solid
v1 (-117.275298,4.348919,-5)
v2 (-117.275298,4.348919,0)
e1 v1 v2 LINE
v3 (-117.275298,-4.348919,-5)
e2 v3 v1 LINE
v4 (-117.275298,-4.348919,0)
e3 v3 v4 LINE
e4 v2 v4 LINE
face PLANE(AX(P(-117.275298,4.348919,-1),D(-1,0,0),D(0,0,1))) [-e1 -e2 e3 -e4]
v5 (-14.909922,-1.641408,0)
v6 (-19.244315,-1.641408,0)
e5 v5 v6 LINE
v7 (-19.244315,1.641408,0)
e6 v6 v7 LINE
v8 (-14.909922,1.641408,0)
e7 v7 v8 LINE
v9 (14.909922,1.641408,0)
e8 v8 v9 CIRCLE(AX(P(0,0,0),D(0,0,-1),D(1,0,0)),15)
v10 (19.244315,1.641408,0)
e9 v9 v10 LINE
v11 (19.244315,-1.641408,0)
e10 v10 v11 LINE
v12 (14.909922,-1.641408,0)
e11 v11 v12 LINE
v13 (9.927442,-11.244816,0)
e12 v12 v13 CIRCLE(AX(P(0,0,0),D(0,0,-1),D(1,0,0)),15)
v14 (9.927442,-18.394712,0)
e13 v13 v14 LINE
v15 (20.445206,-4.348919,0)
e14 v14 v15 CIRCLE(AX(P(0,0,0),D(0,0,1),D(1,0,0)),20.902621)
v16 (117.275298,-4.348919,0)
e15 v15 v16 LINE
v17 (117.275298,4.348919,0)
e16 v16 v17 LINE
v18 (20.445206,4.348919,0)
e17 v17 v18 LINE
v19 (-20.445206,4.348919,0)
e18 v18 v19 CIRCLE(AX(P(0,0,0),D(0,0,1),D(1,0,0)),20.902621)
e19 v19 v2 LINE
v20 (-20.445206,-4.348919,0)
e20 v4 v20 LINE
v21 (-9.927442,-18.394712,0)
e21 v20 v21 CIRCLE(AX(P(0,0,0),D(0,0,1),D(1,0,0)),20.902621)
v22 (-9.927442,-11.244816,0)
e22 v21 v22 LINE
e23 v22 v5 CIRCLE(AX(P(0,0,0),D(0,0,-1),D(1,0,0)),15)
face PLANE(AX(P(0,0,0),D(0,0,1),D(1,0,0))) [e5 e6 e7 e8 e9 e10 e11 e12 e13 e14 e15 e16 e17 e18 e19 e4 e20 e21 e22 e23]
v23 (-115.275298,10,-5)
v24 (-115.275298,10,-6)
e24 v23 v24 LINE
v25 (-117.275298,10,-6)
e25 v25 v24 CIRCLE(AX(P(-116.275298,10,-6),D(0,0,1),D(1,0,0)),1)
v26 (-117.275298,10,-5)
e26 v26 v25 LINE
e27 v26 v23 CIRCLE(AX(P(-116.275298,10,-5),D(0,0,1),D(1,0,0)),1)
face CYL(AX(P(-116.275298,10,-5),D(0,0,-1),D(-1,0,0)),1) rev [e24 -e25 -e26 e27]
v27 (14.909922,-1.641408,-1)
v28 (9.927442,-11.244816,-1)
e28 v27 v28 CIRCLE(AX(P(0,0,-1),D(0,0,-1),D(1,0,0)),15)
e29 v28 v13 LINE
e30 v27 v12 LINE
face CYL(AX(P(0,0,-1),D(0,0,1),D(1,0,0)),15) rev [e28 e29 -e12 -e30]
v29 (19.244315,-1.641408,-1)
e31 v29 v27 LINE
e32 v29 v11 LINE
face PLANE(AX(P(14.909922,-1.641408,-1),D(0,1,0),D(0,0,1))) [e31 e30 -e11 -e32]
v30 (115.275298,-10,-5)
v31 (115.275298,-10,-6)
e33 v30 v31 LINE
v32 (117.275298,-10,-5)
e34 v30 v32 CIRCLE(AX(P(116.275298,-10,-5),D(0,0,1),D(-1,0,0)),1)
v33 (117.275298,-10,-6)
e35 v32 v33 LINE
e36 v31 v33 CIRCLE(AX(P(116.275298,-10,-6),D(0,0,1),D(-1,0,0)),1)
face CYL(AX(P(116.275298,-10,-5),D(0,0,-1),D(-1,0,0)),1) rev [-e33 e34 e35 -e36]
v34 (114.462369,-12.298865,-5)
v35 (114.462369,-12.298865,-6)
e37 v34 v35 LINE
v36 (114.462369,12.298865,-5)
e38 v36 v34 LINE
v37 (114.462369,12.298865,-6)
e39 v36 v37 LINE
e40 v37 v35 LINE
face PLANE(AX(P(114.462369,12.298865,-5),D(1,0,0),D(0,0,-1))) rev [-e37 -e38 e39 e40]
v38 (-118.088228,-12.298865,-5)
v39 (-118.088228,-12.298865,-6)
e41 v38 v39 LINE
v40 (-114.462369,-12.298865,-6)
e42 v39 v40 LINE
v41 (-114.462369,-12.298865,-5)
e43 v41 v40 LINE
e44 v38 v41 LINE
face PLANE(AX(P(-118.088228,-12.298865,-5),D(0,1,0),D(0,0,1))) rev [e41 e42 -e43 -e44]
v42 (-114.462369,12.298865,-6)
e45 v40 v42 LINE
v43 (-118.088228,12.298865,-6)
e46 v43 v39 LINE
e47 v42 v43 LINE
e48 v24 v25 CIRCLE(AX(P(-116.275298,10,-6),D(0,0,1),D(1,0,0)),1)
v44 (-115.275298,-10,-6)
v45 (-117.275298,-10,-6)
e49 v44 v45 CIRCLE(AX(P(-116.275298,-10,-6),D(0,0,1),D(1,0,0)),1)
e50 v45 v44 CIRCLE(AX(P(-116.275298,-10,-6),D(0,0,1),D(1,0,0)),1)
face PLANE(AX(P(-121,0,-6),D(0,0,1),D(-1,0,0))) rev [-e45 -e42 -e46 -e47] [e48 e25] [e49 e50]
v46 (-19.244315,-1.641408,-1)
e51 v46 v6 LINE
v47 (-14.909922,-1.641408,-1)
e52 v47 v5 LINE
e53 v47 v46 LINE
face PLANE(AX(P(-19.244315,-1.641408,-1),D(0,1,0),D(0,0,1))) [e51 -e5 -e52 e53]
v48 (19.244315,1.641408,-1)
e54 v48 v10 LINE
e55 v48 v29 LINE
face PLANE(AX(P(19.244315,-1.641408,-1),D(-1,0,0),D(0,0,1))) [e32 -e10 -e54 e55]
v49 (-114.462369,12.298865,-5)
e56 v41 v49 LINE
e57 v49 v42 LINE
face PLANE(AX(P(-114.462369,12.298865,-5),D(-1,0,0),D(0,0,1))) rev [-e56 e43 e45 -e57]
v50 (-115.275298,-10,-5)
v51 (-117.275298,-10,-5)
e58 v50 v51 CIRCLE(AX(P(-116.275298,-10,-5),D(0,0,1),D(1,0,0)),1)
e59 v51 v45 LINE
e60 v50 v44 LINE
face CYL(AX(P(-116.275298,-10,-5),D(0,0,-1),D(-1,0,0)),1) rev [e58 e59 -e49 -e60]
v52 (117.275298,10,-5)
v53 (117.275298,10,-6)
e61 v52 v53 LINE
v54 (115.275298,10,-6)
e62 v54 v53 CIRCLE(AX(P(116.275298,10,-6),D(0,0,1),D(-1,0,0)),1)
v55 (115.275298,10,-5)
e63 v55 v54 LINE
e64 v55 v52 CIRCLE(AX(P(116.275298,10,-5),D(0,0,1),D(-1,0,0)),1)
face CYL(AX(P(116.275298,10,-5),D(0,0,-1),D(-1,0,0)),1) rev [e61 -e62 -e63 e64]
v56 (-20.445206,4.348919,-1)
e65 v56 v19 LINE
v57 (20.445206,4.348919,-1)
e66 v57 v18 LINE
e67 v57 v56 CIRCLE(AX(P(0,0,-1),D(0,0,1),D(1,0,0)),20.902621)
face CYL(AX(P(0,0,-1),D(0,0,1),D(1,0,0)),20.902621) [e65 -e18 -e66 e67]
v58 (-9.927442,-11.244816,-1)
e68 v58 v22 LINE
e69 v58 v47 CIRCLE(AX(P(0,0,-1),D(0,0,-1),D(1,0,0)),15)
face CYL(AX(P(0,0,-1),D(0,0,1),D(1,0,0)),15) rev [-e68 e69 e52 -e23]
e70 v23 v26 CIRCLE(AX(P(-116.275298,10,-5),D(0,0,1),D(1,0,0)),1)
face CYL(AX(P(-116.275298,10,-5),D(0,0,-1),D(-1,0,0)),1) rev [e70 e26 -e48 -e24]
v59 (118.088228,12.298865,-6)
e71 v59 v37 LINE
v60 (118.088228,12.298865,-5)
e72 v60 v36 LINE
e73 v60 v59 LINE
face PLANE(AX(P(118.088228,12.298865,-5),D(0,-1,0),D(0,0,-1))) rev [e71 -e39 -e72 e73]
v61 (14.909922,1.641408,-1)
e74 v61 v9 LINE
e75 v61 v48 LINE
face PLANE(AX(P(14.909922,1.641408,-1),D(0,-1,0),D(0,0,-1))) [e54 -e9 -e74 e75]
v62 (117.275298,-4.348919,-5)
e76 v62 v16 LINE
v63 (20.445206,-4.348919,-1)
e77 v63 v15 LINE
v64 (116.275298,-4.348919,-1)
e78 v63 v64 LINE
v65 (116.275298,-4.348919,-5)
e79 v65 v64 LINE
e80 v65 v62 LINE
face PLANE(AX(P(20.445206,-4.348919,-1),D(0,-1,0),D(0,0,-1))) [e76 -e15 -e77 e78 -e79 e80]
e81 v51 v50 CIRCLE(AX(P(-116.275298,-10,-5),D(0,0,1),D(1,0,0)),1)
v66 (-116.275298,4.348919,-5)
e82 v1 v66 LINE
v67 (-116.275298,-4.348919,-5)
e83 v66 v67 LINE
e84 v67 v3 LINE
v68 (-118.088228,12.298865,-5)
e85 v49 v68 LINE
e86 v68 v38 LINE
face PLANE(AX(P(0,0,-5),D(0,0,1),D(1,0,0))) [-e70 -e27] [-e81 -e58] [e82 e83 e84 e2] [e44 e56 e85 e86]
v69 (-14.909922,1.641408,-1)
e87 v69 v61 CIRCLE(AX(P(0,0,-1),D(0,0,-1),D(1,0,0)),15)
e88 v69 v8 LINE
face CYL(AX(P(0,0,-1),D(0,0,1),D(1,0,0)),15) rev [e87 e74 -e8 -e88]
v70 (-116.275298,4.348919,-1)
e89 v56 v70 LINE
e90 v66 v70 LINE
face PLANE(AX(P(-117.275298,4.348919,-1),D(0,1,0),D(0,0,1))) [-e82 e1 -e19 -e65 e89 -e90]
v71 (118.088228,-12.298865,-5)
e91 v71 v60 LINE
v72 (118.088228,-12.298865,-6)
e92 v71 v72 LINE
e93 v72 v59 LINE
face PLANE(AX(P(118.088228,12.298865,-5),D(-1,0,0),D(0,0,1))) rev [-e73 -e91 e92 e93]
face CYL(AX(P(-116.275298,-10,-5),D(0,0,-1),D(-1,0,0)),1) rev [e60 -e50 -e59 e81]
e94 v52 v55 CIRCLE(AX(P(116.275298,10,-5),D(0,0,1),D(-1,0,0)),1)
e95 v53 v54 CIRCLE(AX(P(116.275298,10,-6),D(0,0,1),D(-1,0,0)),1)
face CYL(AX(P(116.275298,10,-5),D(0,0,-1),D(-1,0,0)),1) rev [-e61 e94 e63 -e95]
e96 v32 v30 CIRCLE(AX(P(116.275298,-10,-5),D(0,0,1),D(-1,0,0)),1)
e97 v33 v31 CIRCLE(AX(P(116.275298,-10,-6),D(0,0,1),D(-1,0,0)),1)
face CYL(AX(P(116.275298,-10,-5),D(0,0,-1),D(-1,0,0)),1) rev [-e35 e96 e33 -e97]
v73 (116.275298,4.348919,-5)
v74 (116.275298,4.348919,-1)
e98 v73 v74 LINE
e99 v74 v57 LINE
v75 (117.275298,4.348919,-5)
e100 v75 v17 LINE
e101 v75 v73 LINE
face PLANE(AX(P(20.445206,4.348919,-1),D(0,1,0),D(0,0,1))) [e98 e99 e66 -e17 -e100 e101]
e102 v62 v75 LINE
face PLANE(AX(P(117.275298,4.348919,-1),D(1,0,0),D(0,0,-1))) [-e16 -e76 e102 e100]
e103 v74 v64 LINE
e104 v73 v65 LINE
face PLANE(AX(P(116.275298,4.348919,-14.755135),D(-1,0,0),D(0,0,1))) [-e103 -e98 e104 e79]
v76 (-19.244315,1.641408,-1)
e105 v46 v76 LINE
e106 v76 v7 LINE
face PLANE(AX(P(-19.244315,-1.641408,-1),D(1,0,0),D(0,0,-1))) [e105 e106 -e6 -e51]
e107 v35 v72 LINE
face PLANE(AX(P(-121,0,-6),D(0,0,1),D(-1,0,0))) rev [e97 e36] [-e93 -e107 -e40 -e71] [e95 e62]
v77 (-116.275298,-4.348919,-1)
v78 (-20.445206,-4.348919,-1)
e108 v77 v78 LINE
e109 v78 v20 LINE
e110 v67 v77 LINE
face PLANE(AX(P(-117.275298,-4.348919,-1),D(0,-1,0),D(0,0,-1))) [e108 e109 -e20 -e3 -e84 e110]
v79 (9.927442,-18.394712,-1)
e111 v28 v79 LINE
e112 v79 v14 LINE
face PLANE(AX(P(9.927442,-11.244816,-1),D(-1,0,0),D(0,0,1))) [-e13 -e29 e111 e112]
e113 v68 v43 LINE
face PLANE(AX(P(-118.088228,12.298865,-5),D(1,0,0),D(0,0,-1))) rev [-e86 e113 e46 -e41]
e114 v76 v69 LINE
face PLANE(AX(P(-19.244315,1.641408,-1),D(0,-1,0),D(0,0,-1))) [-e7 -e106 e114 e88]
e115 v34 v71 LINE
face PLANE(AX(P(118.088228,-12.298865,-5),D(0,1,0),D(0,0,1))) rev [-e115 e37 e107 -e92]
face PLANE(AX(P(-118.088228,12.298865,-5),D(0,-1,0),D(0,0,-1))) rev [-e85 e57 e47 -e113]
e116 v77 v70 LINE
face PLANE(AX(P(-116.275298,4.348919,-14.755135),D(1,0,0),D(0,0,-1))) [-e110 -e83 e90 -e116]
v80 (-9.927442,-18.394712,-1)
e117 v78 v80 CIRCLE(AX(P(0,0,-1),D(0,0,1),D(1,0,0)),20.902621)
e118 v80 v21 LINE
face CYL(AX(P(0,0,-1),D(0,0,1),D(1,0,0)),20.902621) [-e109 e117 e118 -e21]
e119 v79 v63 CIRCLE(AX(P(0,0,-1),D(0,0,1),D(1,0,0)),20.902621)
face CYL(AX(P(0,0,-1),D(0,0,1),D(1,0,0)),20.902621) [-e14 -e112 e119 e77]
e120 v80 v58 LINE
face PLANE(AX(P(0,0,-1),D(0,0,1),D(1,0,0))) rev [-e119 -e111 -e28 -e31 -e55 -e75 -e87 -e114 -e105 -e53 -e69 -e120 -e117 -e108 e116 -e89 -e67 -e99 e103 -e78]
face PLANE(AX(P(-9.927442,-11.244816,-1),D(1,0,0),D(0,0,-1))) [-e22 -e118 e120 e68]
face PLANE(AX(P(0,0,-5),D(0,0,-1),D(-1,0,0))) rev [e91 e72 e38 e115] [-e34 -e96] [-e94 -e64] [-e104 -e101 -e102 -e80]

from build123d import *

# Parameters (mm, degrees)
BOSS_EXTRUDE1_DEPTH = 1
SKETCH2_W           = 1
SKETCH2_H           = 8.697838108
BOSS_EXTRUDE2_DEPTH = 6
SKETCH3_W           = 3.625858974
SKETCH3_H           = 24.597729298
SKETCH3_R           = 1
BOSS_EXTRUDE3_DEPTH = 1


with BuildPart() as part:
    # Sketch1 → Boss-Extrude1 (new body)
    with BuildSketch(Plane.XY):
        with BuildLine():
            Line((117.275298476, 4.348919054), (20.445206114, 4.348919054))
            ThreePointArc((20.445206114, 4.348919054), (0, 20.902620649), (-20.445206114, 4.348919054))
            Line((-20.445206114, 4.348919054), (-117.275298476, 4.348919054))
            Line((-117.275298476, 4.348919054), (-117.275298476, -4.348919054))
            Line((-117.275298476, -4.348919054), (-20.445206114, -4.348919054))
            ThreePointArc((-20.445206114, -4.348919054), (-16.73157253, -12.528927754), (-9.927442271, -18.394712283))
            Line((-9.927442271, -18.394712283), (-9.927442271, -11.244816137))
            ThreePointArc((-9.927442271, -11.244816137), (-13.314654662, -6.907964333), (-14.909922164, -1.641408252))
            Line((-14.909922164, -1.641408252), (-19.244314933, -1.641408252))
            Line((-19.244314933, -1.641408252), (-19.244314933, 1.641408252))
            Line((-19.244314933, 1.641408252), (-14.909922164, 1.641408252))
            ThreePointArc((-14.909922164, 1.641408252), (0, 15), (14.909922164, 1.641408252))
            Line((14.909922164, 1.641408252), (19.244314933, 1.641408252))
            Line((19.244314933, 1.641408252), (19.244314933, -1.641408252))
            Line((19.244314933, -1.641408252), (14.909922164, -1.641408252))
            ThreePointArc((14.909922164, -1.641408252), (13.314654662, -6.907964333), (9.927442271, -11.244816137))
            Line((9.927442271, -11.244816137), (9.927442271, -18.394712283))
            ThreePointArc((9.927442271, -18.394712283), (16.73157253, -12.528927754), (20.445206114, -4.348919054))
            Line((20.445206114, -4.348919054), (117.275298476, -4.348919054))
            Line((117.275298476, -4.348919054), (117.275298476, 4.348919054))
        make_face()
    extrude(amount=-BOSS_EXTRUDE1_DEPTH)

    # Sketch2 → Boss-Extrude2 (add)
    with BuildSketch(Plane.XY):
        with Locations((-116.775298476, 0)):
            Rectangle(SKETCH2_W, SKETCH2_H)
        with Locations((116.775298476, 0)):
            Rectangle(SKETCH2_W, SKETCH2_H)
    extrude(amount=-BOSS_EXTRUDE2_DEPTH)

    # Sketch3 → Boss-Extrude3 (add)
    # profile 1 of 2: a face of its own
    with BuildSketch(Plane.XY.offset(-6)):
        with Locations((-116.275298476, 0)):
            Rectangle(SKETCH3_W, SKETCH3_H)
        with Locations((-116.275298476, -10)):
            Circle(SKETCH3_R, mode=Mode.SUBTRACT)
        with Locations((-116.275298476, 10)):
            Circle(SKETCH3_R, mode=Mode.SUBTRACT)
    # profile 2 of 2: a face of its own
    with BuildSketch(Plane.XY.offset(-6)):
        with Locations((116.275298476, 0)):
            Rectangle(SKETCH3_W, SKETCH3_H)
        with Locations(Location((116.275298476, 10, 0), (0, 0, 180))):
            Circle(SKETCH3_R, mode=Mode.SUBTRACT)
        with Locations(Location((116.275298476, -10, 0), (0, 0, 180))):
            Circle(SKETCH3_R, mode=Mode.SUBTRACT)
    extrude(amount=BOSS_EXTRUDE3_DEPTH)


solid = part.part
